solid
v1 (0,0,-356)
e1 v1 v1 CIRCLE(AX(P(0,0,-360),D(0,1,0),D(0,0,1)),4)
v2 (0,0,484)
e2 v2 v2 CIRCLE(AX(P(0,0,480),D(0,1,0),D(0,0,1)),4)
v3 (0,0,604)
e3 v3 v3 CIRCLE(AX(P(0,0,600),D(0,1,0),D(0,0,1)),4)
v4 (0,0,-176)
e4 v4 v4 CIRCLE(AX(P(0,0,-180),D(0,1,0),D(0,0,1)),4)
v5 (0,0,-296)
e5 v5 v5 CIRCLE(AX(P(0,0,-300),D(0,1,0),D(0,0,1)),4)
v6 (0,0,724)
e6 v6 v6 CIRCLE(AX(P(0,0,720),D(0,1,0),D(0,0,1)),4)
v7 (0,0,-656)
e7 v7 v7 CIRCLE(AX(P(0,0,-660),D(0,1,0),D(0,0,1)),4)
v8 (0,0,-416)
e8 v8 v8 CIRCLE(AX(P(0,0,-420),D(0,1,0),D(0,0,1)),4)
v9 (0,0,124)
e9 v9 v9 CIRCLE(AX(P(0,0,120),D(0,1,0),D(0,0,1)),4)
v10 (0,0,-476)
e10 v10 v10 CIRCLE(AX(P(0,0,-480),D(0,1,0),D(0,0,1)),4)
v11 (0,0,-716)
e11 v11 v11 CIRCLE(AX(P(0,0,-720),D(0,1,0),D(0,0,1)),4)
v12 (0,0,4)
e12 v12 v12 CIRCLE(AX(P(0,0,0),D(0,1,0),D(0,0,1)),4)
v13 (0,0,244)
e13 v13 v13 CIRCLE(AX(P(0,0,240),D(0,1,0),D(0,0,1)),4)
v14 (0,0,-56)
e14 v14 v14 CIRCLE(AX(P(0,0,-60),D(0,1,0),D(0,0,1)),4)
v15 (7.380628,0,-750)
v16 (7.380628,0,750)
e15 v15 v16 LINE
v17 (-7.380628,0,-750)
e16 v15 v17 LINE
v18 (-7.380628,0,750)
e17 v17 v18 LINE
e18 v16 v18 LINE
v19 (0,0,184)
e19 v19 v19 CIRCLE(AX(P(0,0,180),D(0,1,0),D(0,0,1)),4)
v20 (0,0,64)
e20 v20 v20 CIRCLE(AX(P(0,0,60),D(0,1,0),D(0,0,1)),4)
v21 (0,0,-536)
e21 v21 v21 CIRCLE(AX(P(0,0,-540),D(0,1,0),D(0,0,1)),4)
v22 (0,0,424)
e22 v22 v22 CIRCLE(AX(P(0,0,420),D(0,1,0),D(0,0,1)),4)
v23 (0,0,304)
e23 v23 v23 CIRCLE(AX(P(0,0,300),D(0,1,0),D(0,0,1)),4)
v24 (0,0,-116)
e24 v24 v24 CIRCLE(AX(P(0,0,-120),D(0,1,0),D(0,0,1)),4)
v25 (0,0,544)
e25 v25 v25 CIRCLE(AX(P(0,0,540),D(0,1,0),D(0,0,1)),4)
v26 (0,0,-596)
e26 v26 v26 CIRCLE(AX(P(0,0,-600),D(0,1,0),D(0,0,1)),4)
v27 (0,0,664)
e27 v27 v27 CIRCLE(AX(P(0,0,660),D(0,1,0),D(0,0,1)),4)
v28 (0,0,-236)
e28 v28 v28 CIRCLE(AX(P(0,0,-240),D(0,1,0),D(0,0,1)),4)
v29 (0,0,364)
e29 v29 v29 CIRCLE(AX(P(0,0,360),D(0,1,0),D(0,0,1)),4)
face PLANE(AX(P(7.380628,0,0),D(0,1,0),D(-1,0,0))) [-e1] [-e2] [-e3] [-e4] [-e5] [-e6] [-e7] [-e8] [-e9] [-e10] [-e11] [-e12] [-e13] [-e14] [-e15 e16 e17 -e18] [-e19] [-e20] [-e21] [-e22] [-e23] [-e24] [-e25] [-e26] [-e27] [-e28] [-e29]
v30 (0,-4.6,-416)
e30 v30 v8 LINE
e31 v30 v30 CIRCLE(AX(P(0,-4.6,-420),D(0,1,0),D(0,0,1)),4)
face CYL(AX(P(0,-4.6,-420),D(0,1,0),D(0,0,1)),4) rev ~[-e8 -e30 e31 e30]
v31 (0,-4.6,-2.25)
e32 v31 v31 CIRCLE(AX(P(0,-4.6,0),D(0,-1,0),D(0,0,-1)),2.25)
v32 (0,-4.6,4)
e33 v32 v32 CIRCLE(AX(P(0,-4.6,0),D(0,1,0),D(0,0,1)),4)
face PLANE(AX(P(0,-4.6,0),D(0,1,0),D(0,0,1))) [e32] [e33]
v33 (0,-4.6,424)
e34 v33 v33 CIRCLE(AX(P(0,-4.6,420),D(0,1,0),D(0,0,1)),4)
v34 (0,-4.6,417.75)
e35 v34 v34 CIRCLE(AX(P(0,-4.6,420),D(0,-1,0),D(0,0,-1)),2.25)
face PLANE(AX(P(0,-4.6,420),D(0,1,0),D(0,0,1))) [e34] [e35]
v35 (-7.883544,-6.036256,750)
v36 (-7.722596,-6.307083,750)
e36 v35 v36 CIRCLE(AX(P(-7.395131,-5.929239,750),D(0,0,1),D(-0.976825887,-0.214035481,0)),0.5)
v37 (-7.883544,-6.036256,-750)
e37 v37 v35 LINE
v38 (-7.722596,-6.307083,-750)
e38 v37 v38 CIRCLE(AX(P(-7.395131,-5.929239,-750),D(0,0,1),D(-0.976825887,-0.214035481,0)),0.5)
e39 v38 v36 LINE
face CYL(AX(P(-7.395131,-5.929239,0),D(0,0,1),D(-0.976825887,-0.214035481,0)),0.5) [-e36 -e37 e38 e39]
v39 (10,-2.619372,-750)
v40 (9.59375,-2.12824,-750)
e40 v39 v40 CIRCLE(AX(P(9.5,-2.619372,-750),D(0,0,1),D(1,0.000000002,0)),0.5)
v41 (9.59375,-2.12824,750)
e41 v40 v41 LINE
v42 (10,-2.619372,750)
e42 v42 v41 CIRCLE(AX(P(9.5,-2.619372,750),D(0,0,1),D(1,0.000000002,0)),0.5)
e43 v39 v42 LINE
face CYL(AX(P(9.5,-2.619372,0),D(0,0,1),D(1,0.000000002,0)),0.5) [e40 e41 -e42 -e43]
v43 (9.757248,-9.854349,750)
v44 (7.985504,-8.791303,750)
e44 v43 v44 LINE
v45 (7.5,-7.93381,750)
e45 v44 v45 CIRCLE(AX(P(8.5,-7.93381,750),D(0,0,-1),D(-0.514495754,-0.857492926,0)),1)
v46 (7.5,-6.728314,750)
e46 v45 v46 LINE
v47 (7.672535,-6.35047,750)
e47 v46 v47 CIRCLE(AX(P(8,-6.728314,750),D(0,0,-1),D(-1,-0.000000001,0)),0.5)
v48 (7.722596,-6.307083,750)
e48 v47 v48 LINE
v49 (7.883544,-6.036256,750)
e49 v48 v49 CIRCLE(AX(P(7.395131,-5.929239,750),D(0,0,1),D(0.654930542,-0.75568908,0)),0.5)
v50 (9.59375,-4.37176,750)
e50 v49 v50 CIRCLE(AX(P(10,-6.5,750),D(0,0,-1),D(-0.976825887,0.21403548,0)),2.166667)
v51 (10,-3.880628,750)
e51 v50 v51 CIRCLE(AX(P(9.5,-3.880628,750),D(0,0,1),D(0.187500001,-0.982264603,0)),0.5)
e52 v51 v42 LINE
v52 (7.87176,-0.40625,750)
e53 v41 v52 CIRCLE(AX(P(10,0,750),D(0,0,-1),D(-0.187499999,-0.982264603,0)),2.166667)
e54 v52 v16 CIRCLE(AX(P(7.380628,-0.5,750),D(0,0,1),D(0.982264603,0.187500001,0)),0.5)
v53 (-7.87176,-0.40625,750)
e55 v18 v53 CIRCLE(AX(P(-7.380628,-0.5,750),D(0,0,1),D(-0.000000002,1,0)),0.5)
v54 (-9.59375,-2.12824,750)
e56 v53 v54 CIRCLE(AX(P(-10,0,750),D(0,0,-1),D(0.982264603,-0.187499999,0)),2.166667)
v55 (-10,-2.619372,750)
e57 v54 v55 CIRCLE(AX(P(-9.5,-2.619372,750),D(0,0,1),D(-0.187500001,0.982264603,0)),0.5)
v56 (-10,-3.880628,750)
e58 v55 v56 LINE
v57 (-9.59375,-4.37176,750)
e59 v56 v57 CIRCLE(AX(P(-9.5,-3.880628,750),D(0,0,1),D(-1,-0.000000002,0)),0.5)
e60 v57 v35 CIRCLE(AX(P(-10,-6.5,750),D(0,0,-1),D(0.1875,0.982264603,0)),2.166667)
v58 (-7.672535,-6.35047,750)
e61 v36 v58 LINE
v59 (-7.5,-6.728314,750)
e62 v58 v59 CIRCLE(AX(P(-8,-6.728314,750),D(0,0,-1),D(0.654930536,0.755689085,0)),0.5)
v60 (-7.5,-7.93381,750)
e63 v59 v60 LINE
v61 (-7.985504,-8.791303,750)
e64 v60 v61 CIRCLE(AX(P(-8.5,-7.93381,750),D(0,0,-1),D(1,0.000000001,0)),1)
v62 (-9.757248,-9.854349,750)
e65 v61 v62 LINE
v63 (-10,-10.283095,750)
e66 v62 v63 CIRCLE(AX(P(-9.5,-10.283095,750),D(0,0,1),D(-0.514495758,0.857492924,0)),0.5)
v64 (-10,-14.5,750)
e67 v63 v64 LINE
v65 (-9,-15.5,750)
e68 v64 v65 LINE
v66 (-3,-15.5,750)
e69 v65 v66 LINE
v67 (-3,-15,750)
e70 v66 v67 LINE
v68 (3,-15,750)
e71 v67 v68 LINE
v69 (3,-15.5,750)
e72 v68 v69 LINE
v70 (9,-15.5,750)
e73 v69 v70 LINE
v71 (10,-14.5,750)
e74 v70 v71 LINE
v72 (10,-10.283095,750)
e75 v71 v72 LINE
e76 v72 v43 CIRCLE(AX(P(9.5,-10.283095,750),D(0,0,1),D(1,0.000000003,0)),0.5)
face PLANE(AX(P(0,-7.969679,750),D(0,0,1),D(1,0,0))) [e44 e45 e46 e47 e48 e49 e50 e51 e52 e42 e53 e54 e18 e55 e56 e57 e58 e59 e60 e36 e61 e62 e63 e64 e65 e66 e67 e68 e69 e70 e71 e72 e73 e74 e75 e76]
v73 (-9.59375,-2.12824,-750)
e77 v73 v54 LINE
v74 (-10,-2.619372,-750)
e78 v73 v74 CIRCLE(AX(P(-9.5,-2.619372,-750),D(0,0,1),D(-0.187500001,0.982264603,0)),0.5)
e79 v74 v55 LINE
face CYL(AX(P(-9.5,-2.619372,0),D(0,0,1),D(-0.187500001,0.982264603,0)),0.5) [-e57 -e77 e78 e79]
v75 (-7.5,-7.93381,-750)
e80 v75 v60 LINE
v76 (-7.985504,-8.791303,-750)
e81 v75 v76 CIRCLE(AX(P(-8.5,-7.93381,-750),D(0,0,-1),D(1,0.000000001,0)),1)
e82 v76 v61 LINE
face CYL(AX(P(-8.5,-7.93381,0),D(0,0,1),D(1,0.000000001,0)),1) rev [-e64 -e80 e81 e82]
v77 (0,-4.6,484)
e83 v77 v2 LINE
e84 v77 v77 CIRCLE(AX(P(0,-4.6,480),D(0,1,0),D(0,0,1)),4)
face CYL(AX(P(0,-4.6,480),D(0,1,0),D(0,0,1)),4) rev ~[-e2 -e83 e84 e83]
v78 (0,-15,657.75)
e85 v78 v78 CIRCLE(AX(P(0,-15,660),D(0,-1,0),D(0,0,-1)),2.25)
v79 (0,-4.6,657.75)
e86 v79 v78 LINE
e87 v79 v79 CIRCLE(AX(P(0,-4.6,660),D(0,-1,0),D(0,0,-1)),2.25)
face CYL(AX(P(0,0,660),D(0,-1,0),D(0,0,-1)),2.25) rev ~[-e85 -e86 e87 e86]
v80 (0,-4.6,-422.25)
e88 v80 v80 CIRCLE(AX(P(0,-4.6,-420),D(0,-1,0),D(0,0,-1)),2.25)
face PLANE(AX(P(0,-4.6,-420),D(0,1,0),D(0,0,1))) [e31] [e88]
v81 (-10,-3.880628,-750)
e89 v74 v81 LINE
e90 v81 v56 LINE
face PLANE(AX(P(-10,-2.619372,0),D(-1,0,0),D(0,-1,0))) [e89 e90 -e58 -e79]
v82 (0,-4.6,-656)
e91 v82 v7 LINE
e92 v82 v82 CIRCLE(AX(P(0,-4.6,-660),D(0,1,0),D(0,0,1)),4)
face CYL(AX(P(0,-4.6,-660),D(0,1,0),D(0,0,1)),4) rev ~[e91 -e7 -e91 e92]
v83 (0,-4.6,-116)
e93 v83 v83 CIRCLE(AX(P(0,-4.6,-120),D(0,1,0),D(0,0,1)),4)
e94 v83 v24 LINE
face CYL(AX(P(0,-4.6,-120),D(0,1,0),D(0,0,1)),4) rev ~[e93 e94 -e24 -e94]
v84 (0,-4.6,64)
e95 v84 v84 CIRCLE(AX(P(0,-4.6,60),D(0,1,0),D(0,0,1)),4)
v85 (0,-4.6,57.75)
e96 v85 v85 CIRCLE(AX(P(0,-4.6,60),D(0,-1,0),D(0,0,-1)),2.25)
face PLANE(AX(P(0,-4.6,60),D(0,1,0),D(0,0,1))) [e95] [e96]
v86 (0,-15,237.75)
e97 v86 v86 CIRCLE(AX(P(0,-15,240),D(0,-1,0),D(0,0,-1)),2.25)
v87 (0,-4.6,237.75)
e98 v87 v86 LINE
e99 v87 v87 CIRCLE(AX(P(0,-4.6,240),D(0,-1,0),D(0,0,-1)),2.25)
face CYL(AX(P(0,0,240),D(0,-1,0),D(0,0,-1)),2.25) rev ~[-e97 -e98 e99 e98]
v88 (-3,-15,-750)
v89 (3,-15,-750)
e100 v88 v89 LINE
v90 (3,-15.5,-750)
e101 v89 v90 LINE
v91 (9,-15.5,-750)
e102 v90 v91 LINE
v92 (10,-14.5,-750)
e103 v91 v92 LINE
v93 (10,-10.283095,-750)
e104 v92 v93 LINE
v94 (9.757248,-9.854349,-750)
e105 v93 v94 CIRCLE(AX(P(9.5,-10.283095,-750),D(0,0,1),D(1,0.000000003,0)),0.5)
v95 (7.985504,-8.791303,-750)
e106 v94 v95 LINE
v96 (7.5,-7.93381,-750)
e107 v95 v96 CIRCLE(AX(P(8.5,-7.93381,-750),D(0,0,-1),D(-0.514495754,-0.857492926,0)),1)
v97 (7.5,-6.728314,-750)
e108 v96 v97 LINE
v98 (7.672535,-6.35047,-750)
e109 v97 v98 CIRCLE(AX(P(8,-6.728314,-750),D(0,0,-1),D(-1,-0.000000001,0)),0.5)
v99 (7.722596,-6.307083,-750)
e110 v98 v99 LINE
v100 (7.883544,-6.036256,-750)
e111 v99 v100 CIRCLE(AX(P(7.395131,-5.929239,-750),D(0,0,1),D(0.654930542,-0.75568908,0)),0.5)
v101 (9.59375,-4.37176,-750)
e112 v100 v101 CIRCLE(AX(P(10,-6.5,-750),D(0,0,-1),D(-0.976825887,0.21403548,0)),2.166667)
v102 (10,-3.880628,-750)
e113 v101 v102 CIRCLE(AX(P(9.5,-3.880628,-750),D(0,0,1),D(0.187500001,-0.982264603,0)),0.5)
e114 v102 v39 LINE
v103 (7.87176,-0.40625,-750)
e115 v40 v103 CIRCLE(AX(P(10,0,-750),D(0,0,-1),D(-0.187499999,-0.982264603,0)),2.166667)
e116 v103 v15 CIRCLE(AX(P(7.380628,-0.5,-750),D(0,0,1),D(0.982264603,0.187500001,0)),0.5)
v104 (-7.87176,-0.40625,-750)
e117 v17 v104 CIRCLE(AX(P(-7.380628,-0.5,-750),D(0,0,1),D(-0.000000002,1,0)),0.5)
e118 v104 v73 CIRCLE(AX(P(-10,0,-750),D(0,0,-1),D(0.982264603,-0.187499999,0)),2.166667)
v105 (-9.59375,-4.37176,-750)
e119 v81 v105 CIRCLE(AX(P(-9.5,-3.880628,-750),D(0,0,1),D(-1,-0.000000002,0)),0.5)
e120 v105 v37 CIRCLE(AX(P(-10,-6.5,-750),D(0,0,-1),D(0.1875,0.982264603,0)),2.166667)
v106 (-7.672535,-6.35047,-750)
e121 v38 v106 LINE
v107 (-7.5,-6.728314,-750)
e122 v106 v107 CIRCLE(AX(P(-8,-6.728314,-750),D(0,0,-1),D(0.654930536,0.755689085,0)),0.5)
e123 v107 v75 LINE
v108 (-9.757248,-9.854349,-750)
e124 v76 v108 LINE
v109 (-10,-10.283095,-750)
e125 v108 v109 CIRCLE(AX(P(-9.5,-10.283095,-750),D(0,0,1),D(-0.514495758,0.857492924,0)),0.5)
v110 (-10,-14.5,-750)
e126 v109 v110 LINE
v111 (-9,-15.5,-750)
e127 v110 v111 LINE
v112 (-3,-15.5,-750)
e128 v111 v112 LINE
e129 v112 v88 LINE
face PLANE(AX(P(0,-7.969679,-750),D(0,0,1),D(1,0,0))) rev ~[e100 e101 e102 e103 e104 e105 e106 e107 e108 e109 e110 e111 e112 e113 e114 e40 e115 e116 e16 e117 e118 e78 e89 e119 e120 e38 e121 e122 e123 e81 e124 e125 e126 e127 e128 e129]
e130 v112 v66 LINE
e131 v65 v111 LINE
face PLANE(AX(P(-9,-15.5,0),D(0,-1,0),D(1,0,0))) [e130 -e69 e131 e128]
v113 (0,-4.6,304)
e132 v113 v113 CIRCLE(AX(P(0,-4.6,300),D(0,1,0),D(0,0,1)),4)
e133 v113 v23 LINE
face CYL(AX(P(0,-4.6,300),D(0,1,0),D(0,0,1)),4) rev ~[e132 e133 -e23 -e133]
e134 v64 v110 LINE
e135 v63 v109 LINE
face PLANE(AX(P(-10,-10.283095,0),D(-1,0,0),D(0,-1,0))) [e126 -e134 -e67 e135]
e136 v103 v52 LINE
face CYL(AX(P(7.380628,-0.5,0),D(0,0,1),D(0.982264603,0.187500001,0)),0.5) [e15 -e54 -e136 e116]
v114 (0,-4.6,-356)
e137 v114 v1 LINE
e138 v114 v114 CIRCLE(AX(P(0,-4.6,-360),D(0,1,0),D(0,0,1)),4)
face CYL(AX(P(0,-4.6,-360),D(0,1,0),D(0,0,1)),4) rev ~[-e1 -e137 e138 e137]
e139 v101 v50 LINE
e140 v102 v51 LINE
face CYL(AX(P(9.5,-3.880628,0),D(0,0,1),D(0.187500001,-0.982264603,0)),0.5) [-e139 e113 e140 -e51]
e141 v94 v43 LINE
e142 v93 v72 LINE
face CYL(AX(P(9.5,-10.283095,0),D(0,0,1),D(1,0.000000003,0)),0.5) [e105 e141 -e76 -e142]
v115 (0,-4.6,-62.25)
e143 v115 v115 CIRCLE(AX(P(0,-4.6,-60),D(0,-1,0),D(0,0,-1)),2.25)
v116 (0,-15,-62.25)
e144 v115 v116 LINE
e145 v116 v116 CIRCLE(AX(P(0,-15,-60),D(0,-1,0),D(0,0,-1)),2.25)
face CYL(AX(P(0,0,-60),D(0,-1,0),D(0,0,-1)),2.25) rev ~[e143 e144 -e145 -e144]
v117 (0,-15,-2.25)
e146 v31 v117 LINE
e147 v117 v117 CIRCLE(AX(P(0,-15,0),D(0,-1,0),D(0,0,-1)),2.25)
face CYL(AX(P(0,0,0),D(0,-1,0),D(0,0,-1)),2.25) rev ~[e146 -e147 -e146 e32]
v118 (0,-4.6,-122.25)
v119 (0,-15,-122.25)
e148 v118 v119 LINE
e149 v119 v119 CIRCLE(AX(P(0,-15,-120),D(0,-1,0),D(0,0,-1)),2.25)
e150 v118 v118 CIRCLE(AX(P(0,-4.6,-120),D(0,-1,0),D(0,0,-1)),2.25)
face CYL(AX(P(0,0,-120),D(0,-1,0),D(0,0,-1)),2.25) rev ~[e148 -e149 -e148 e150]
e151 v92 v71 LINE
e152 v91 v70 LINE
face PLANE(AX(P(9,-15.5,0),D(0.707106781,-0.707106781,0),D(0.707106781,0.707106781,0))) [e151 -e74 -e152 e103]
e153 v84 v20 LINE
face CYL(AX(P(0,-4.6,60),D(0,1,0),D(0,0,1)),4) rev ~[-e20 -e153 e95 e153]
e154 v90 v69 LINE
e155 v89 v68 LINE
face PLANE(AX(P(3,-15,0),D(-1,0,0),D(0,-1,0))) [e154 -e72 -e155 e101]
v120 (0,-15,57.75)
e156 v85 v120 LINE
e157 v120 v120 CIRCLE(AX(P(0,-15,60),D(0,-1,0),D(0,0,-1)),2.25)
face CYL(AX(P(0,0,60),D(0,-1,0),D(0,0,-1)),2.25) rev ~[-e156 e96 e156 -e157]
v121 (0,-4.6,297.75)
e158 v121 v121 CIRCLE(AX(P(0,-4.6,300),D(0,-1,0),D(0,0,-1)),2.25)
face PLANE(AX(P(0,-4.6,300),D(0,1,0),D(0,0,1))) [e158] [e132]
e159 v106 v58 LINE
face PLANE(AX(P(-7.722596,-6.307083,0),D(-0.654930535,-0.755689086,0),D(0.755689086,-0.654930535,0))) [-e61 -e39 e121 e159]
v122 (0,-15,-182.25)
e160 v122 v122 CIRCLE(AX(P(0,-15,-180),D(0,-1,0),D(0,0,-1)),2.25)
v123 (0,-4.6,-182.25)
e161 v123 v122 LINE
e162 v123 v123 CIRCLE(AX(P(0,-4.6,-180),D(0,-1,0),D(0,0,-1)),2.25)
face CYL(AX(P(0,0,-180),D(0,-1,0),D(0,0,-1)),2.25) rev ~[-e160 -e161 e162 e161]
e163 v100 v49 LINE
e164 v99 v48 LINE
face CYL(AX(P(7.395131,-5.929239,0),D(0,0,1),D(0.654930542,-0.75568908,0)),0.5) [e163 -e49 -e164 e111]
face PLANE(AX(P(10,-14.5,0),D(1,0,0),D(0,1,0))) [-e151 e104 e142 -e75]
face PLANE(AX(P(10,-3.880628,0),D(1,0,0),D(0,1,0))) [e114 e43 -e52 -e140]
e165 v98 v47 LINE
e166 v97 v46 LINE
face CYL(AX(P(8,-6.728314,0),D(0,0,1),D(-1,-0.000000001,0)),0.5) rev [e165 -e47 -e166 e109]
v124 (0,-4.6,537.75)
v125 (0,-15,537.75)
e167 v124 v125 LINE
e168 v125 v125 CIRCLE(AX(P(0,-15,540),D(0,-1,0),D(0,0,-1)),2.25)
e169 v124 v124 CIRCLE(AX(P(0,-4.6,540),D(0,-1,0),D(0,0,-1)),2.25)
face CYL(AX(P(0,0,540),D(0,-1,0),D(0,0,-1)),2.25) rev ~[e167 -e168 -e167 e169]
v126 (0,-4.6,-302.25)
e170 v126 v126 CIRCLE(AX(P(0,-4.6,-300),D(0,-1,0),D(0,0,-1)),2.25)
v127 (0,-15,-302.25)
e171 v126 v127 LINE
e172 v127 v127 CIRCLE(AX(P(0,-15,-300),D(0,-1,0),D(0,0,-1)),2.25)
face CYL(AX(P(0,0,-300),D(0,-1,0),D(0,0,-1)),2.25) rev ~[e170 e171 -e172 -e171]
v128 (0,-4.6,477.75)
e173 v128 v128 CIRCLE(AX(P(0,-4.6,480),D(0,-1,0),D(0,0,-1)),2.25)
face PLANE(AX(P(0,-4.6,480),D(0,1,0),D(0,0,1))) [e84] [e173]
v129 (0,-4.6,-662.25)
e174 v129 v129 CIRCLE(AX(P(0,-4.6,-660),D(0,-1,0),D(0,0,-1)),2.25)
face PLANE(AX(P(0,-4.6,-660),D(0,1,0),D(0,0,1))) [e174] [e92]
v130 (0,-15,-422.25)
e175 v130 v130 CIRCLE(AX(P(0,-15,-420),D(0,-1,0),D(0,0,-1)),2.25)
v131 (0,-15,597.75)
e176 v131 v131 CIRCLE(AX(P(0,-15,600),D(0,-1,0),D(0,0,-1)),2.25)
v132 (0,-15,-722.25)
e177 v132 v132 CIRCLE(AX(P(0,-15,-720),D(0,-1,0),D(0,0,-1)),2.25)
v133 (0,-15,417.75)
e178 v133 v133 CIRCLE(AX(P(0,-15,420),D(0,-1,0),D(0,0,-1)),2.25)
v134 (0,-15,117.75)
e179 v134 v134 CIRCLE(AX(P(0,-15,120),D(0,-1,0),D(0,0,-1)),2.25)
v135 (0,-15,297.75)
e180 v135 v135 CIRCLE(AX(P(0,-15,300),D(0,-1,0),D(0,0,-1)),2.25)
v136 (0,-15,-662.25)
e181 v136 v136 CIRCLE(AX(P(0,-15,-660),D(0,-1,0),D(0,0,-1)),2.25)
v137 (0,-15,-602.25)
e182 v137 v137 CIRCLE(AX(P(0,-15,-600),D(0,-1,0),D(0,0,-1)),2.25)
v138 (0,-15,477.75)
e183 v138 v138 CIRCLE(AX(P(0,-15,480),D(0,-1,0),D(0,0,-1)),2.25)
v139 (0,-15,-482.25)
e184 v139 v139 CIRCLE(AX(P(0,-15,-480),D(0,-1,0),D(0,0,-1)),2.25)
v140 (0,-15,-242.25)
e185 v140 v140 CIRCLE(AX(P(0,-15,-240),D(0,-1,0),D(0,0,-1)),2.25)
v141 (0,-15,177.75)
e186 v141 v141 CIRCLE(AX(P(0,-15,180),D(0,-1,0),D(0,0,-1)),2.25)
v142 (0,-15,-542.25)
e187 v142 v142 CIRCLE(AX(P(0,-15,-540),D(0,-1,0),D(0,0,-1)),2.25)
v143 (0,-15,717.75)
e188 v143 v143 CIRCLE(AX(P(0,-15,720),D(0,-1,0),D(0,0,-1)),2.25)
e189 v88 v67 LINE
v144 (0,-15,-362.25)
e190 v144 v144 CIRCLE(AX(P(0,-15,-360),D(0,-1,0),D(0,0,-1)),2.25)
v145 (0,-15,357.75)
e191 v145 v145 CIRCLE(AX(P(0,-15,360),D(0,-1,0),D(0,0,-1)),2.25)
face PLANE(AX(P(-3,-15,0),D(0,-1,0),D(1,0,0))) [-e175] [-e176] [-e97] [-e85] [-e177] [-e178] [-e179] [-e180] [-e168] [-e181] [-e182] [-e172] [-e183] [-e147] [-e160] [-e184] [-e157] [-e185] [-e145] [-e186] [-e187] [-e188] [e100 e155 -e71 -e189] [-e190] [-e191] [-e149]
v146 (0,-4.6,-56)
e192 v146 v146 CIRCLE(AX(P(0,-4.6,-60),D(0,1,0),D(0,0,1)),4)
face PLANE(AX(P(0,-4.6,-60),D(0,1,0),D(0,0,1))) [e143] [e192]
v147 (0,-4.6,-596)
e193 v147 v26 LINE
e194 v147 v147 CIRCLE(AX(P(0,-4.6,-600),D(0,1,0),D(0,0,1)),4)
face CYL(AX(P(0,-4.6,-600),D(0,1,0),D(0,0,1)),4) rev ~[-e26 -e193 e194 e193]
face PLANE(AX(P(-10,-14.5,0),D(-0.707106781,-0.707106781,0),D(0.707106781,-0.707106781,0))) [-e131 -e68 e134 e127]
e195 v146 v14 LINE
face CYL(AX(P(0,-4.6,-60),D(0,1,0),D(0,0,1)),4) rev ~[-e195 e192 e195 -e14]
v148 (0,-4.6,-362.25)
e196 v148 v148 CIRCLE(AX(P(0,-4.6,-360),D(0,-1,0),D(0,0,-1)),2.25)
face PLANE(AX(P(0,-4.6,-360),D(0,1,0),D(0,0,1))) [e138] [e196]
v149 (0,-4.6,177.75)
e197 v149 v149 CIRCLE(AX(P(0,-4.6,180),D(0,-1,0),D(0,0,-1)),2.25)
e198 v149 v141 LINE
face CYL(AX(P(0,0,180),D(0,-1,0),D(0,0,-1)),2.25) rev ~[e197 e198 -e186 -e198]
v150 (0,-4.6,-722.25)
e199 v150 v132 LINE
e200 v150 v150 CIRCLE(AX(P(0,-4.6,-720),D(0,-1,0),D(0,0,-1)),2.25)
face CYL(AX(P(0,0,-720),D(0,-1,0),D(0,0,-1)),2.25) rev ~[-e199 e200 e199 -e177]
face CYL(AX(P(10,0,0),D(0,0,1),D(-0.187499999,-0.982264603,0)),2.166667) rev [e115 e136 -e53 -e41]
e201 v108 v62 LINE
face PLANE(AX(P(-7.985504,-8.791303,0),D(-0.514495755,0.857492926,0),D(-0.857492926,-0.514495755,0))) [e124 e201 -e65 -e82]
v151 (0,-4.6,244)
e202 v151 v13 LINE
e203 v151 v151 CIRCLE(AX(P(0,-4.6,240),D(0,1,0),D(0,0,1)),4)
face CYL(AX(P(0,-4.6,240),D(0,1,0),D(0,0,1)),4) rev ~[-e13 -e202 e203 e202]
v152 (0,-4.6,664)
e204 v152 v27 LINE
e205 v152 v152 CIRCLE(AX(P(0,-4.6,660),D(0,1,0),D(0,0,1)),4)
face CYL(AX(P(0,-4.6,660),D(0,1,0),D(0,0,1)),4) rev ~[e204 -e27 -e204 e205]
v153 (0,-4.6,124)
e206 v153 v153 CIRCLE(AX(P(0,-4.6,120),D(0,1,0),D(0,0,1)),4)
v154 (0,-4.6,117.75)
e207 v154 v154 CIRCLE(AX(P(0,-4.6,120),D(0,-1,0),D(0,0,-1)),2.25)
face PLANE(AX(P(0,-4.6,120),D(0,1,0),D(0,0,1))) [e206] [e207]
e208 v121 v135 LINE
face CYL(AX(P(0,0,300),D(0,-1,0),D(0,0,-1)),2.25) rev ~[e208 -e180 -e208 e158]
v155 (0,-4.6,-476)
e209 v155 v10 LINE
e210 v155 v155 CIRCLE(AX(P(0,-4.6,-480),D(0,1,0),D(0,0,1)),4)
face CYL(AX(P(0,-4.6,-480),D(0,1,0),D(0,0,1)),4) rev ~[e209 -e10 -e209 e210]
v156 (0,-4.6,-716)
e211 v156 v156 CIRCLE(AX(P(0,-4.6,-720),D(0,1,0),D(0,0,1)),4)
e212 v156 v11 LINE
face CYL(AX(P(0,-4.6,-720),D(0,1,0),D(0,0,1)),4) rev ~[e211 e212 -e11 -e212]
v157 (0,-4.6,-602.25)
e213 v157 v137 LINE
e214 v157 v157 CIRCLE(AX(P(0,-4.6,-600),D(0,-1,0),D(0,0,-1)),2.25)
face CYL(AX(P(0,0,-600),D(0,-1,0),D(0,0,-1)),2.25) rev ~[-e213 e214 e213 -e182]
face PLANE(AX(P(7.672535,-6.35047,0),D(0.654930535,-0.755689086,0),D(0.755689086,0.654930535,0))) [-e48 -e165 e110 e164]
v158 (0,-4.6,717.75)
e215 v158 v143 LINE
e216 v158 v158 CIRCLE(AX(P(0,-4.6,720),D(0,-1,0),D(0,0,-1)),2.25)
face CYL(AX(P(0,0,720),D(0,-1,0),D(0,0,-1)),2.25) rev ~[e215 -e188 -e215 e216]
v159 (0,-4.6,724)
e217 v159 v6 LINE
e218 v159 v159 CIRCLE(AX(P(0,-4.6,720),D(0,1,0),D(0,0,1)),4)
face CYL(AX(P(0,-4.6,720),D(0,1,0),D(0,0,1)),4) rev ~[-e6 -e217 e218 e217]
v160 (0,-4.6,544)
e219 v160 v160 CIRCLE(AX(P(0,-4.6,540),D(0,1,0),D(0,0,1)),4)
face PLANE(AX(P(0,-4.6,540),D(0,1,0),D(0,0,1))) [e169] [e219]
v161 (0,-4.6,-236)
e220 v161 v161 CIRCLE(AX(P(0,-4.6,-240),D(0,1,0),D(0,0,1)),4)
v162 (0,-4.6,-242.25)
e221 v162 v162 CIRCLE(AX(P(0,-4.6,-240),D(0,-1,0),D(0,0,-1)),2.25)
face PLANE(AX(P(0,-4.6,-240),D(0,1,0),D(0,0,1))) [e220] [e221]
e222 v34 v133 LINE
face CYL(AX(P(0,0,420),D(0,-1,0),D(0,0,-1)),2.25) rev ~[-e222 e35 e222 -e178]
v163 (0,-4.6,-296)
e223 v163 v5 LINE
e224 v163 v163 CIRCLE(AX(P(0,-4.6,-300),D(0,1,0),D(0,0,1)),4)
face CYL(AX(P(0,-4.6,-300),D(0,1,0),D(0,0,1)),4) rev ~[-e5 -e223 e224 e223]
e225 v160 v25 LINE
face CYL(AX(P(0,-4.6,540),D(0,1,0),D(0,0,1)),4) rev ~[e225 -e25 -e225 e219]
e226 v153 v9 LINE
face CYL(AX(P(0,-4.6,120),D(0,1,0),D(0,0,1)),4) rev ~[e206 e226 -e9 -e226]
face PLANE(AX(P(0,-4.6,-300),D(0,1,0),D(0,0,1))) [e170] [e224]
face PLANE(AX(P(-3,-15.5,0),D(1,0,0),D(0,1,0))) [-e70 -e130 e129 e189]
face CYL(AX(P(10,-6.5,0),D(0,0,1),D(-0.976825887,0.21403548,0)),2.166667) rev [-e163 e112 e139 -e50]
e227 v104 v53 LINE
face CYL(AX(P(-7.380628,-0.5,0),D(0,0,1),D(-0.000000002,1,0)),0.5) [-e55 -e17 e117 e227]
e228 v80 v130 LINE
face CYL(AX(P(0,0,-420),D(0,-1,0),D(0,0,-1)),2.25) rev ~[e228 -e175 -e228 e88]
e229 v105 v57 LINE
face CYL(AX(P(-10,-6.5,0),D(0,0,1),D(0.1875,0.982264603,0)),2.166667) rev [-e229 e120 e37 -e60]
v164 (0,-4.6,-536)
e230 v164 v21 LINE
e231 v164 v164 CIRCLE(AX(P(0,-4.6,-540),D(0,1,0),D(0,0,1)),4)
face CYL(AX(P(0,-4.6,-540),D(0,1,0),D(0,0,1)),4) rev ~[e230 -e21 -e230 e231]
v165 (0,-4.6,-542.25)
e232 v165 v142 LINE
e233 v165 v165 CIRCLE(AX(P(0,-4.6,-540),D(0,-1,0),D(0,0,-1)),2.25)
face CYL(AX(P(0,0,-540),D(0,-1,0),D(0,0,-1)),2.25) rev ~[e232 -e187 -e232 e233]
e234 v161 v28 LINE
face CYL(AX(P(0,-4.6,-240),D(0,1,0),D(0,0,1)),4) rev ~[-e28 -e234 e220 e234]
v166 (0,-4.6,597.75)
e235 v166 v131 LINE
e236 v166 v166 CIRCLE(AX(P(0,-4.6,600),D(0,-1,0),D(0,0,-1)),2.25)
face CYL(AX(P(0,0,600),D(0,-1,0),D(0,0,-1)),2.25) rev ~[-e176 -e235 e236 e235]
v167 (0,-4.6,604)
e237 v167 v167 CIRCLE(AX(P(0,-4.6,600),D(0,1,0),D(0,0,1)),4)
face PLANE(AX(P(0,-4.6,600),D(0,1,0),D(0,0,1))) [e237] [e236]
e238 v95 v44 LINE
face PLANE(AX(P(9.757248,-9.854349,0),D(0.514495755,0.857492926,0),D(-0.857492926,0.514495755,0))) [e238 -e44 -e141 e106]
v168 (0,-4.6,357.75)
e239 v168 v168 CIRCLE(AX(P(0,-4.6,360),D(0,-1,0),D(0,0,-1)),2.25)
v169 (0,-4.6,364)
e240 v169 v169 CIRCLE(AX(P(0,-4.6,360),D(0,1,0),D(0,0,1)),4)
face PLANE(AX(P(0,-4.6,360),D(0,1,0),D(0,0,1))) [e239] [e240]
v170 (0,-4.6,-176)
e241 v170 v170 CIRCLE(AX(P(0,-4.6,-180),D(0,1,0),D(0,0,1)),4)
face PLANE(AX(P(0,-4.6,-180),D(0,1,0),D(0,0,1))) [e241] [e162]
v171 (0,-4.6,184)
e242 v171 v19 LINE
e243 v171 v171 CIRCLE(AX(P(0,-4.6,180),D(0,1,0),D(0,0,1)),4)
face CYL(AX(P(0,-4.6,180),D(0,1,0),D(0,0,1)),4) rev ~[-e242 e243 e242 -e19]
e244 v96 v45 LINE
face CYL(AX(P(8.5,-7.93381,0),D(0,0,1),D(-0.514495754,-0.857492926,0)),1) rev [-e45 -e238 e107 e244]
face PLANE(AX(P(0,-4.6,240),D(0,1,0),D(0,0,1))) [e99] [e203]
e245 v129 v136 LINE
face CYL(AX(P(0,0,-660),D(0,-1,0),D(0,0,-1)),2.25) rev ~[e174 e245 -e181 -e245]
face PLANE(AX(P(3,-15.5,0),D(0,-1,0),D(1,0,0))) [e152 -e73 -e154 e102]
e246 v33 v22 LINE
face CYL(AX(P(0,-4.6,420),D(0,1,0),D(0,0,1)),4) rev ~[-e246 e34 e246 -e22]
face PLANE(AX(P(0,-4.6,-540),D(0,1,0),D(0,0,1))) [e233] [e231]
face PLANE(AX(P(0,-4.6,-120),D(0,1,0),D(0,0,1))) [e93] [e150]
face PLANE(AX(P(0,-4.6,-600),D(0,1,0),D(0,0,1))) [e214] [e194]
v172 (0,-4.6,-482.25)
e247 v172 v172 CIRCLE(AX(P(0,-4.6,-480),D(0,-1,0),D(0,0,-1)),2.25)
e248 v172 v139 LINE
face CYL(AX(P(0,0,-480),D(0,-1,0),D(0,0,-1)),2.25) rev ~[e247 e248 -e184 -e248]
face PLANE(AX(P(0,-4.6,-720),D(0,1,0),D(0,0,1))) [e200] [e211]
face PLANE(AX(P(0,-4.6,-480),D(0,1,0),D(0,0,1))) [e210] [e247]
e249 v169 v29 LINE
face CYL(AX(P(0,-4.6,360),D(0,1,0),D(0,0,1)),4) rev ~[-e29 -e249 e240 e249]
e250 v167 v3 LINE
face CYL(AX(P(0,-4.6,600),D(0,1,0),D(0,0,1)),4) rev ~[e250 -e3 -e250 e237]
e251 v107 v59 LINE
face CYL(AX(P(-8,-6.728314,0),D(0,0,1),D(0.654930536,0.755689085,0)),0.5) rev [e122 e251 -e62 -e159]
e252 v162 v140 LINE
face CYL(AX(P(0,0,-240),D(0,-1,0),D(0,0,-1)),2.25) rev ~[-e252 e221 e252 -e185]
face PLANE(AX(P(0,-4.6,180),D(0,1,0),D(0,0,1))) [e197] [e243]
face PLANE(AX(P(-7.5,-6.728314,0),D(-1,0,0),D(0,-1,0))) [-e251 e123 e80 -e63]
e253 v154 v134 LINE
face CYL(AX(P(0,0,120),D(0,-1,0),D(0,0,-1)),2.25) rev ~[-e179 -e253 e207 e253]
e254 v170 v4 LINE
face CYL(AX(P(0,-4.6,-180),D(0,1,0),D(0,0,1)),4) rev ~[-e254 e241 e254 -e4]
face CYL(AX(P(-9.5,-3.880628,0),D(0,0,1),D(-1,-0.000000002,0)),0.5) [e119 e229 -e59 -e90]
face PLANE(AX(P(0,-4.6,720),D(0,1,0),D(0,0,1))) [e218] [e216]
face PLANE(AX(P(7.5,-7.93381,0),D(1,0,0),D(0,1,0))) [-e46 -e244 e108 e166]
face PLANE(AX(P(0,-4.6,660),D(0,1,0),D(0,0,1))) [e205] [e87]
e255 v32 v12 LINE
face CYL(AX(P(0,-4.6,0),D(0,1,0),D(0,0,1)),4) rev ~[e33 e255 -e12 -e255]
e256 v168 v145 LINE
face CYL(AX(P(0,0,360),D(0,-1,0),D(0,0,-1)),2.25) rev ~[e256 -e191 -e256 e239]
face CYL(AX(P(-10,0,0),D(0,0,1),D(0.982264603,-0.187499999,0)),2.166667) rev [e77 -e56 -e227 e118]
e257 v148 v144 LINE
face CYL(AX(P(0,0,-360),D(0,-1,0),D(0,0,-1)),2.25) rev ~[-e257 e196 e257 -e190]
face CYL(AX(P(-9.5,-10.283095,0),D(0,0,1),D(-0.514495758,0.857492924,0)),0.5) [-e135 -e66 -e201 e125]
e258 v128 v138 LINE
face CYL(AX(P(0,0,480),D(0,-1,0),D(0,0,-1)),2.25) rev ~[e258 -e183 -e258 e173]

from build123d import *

# Parameters (mm, degrees)
EXTRUDE_1_DEPTH           = 750
HOLE_WIZARD_1_D           = 4.5
HOLE_WIZARD_1_CBORE_D     = 8
HOLE_WIZARD_1_CBORE_DEPTH = 4.6
PATTERN_LINEAR_1_COUNT    = 25
PATTERN_LINEAR_1_PITCH    = 60


with BuildPart() as part:
    # 草图1 → 凸台-拉伸1 (new, symmetric)
    with BuildSketch(Plane.XY):
        with BuildLine():
            Line((-9, -15.5), (-3, -15.5))
            Line((-3, -15.5), (-3, -15))
            Line((-3, -15), (3, -15))
            Line((3, -15), (3, -15.5))
            Line((3, -15.5), (9, -15.5))
            Line((9, -15.5), (10, -14.5))
            Line((10, -14.5), (10, -10.283095189))
            ThreePointArc((10, -10.283095189), (9.935099953, -10.036745782), (9.757247878, -9.854348727))
            Line((9.757247878, -9.854348727), (7.985504245, -8.791302547))
            ThreePointArc((7.985504245, -8.791302547), (7.629800093, -8.426508436), (7.5, -7.933809621))
            Line((7.5, -7.933809621), (7.5, -6.728314441))
            ThreePointArc((7.5, -6.728314441), (7.54517441, -6.52062794), (7.672534731, -6.3504699))
            Line((7.672534731, -6.3504699), (7.722596238, -6.307083261))
            ThreePointArc((7.722596238, -6.307083261), (7.824957798, -6.184677355), (7.883543912, -6.036256459))
            ThreePointArc((7.883543912, -6.036256459), (8.488825425, -4.947326226), (9.59375, -4.371760027))
            ThreePointArc((9.59375, -4.371760027), (9.885275875, -4.199316445), (10, -3.880627726))
            Line((10, -3.880627726), (10, -2.619372274))
            ThreePointArc((10, -2.619372274), (9.885275875, -2.300683555), (9.59375, -2.128239973))
            ThreePointArc((9.59375, -2.128239973), (8.467935307, -1.532064693), (7.871760027, -0.40625))
            ThreePointArc((7.871760027, -0.40625), (7.699316445, -0.114724125), (7.380627726, 0))
            Line((7.380627726, 0), (-7.380627726, 0))
            ThreePointArc((-7.380627726, 0), (-7.699316445, -0.114724125), (-7.871760027, -0.40625))
            ThreePointArc((-7.871760027, -0.40625), (-8.467935307, -1.532064693), (-9.59375, -2.128239973))
            ThreePointArc((-9.59375, -2.128239973), (-9.885275875, -2.300683555), (-10, -2.619372274))
            Line((-10, -2.619372274), (-10, -3.880627726))
            ThreePointArc((-10, -3.880627726), (-9.885275875, -4.199316445), (-9.59375, -4.371760027))
            ThreePointArc((-9.59375, -4.371760027), (-8.488825425, -4.947326226), (-7.883543912, -6.036256459))
            ThreePointArc((-7.883543912, -6.036256459), (-7.824957798, -6.184677355), (-7.722596238, -6.307083261))
            Line((-7.722596238, -6.307083261), (-7.672534731, -6.3504699))
            ThreePointArc((-7.672534731, -6.3504699), (-7.54517441, -6.52062794), (-7.5, -6.728314441))
            Line((-7.5, -6.728314441), (-7.5, -7.933809621))
            ThreePointArc((-7.5, -7.933809621), (-7.629800093, -8.426508436), (-7.985504245, -8.791302547))
            Line((-7.985504245, -8.791302547), (-9.757247878, -9.854348727))
            ThreePointArc((-9.757247878, -9.854348727), (-9.935099953, -10.036745782), (-10, -10.283095189))
            Line((-10, -10.283095189), (-10, -14.5))
            Line((-10, -14.5), (-9, -15.5))
        make_face()
    extrude(amount=EXTRUDE_1_DEPTH, both=True)

    # 打孔尺寸(%根据)内六角圆柱头螺钉的类型1 (through all)
    with Locations(Plane(origin=(0, 0, 720), x_dir=(0, 0, 1), z_dir=(0, 1, 0))):
        with Locations((0, 0)):
            hole_wizard_1 = CounterBoreHole(HOLE_WIZARD_1_D / 2, HOLE_WIZARD_1_CBORE_D / 2, HOLE_WIZARD_1_CBORE_DEPTH)

    # 阵列(线性)1: 打孔尺寸(%根据)内六角圆柱头螺钉的类型1 ×25
    with Locations(*[(0, 0, -i * PATTERN_LINEAR_1_PITCH) for i in range(1, PATTERN_LINEAR_1_COUNT)]):
        add(hole_wizard_1, mode=Mode.SUBTRACT)


solid = part.part
